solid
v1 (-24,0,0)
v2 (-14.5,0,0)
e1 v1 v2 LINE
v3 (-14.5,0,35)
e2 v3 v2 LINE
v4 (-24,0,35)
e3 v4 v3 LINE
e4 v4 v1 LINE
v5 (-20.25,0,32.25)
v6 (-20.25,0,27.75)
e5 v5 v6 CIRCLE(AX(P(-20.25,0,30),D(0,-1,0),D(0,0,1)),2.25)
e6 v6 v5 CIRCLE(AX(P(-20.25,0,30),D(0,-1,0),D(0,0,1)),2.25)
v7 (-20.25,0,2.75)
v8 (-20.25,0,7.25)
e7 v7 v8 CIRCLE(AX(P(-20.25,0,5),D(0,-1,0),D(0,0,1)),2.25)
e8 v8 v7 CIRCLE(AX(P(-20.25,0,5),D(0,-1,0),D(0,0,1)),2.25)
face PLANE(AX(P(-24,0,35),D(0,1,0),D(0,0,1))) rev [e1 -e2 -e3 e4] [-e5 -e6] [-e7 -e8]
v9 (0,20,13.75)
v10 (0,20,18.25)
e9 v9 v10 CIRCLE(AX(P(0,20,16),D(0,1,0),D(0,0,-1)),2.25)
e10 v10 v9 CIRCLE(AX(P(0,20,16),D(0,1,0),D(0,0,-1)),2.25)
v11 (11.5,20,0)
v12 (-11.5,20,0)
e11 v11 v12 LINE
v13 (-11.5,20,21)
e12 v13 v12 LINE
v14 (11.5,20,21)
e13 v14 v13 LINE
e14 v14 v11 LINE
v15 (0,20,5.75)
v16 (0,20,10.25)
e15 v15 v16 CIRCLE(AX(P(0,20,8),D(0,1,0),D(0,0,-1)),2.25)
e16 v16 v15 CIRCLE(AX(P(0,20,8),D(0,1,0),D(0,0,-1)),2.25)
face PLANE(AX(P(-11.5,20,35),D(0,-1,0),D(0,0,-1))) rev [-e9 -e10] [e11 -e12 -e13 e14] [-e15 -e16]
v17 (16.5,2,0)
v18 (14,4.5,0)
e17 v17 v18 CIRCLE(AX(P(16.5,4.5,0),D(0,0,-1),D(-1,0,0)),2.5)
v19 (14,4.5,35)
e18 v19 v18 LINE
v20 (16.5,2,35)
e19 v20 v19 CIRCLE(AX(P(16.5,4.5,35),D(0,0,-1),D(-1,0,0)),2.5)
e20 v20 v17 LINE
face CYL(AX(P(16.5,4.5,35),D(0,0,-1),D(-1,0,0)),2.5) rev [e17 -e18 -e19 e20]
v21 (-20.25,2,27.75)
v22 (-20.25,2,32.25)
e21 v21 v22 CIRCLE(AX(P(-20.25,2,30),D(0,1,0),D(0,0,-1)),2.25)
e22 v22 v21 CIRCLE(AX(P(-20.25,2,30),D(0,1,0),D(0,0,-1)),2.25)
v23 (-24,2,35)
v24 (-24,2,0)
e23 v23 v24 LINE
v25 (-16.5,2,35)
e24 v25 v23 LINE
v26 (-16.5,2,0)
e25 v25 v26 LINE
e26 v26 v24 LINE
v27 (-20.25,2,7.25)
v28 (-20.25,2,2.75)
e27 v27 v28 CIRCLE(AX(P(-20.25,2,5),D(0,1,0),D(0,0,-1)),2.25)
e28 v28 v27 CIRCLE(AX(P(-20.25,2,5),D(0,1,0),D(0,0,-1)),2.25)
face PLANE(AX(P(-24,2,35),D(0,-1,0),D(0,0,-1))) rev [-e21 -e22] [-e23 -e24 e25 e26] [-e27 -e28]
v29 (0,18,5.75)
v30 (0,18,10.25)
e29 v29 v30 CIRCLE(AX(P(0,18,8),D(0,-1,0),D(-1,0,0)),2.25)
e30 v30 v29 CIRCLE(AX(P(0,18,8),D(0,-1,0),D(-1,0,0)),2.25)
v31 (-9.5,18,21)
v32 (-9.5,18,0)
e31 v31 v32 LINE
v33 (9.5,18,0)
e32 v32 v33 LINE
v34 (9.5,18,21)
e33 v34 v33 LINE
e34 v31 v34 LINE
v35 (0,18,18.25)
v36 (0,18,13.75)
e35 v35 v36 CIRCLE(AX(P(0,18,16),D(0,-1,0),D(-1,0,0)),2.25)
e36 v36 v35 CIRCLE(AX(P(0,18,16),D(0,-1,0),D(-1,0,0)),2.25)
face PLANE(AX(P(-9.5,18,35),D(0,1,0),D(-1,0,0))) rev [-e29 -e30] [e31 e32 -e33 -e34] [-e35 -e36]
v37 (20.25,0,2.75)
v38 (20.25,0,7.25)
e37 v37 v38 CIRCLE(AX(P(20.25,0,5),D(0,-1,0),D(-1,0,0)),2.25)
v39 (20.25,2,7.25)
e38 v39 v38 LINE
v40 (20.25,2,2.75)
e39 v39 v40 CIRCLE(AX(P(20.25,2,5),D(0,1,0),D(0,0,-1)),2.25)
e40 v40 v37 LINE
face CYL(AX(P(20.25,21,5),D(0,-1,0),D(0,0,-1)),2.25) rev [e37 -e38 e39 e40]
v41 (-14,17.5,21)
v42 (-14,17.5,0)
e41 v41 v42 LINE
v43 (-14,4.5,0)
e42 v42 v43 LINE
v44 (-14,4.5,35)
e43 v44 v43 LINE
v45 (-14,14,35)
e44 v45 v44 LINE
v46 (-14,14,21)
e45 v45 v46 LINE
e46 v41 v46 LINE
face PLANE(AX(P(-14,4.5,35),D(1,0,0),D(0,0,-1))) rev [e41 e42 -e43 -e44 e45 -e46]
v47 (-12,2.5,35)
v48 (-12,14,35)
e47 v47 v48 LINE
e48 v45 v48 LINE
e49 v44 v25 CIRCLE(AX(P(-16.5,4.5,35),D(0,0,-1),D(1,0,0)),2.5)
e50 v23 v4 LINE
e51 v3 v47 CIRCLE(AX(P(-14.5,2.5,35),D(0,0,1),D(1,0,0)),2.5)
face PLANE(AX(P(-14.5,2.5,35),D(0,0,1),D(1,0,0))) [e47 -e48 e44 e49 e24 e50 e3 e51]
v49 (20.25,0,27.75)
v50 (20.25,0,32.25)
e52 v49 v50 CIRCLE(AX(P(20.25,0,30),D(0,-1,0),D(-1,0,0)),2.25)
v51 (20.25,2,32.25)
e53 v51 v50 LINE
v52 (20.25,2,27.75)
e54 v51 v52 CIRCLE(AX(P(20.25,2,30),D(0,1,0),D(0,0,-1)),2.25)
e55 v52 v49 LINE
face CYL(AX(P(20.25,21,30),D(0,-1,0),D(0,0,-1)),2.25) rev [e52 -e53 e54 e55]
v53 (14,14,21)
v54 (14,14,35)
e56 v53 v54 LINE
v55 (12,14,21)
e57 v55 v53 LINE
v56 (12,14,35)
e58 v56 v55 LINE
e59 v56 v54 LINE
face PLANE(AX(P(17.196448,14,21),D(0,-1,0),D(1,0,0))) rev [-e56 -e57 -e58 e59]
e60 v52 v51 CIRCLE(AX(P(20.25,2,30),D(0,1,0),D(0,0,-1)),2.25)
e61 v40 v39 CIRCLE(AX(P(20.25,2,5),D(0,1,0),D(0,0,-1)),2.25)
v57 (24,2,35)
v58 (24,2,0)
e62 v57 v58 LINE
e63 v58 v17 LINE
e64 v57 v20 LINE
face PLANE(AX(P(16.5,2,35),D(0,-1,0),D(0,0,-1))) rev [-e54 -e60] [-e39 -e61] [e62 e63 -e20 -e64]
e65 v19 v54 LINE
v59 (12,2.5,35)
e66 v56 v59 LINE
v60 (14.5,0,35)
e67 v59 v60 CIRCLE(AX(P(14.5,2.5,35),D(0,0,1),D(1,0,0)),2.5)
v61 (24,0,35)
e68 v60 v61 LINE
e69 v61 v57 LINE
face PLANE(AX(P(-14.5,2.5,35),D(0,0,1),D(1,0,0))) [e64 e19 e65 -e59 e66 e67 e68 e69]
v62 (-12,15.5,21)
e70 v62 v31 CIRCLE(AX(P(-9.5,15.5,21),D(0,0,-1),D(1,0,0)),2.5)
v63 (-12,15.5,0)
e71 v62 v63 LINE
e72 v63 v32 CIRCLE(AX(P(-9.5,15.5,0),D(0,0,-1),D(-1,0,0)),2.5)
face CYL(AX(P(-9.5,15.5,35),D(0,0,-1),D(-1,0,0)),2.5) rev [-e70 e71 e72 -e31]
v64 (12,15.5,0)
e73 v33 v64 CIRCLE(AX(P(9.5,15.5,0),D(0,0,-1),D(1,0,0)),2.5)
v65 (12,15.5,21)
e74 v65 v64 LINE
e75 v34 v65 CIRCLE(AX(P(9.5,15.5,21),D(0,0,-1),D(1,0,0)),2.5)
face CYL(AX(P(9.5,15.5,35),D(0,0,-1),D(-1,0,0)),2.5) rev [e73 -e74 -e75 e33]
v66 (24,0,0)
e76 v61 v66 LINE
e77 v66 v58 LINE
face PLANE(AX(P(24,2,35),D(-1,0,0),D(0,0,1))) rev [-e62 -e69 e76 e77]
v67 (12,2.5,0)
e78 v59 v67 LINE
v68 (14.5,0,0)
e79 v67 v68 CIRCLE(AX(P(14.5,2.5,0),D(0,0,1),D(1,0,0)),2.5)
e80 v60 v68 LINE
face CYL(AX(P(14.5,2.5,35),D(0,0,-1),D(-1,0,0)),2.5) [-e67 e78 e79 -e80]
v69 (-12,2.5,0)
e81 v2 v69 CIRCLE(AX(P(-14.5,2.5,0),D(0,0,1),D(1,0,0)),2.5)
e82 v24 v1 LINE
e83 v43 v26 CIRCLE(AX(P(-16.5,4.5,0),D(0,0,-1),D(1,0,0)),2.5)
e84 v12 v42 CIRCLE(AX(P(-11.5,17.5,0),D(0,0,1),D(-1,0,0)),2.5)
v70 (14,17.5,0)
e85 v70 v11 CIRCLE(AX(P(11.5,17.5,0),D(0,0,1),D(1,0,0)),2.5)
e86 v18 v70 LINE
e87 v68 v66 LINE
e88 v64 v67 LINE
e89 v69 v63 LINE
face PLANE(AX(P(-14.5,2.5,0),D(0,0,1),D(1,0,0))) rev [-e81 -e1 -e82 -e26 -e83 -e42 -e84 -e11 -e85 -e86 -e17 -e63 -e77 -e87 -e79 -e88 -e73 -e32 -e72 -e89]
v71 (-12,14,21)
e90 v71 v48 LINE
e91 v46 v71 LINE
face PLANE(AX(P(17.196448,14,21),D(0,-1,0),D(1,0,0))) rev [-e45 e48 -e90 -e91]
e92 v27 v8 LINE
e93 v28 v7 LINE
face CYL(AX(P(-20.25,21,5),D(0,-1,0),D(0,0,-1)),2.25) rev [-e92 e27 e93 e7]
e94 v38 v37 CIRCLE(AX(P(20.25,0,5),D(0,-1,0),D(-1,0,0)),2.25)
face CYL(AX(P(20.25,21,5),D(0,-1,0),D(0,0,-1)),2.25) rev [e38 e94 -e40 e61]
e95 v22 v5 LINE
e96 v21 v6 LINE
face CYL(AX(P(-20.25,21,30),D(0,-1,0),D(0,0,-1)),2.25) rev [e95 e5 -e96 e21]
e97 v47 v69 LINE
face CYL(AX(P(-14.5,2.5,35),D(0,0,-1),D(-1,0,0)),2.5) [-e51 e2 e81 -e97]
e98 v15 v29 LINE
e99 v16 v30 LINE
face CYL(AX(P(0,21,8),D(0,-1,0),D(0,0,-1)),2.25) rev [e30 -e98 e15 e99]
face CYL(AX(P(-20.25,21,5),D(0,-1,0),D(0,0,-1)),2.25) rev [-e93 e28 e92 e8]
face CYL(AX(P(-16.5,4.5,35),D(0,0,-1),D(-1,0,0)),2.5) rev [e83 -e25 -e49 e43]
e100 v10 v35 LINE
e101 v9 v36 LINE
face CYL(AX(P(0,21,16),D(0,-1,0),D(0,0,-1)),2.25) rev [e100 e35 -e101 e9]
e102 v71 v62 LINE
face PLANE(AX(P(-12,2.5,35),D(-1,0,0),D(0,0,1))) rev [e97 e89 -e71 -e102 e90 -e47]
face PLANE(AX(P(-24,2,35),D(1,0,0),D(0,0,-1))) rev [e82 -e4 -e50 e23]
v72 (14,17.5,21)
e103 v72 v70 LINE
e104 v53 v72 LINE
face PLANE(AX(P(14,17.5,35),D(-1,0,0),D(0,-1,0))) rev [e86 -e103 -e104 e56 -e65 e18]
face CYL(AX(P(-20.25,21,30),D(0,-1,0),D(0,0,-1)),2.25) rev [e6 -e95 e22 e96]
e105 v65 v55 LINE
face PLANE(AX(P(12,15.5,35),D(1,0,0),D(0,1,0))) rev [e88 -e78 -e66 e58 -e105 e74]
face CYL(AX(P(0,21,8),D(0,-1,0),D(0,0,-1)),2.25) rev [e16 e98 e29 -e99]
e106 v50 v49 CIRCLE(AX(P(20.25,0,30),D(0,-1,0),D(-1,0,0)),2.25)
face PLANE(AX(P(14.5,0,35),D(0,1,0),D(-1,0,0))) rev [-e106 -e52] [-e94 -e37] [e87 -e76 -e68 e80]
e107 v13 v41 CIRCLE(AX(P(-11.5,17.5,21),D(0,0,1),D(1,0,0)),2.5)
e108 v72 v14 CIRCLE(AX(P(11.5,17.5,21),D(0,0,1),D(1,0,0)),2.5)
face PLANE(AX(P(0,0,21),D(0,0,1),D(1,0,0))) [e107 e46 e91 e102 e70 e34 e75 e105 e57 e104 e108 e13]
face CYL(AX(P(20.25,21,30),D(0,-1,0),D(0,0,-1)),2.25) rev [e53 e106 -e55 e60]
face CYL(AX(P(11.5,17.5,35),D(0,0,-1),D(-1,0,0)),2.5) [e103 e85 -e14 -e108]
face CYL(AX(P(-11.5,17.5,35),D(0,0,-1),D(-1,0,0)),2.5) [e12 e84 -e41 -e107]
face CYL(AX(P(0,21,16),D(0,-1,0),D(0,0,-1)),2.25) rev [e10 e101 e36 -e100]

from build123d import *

# Parameters (mm, degrees)
BOSS_EXTRUDE1_DEPTH = 35
SKETCH2_W           = 34.392896322
SKETCH2_H           = 15.037586703
CUT_EXTRUDE1_DEPTH  = 14
SKETCH3_R           = 2.25
CUT_EXTRUDE2_DEPTH  = 19


with BuildPart() as part:
    # Sketch1 → Boss-Extrude1 (new body)
    with BuildSketch(Plane.XY):
        with BuildLine():
            Line((-24, 0), (-14.5, 0))
            ThreePointArc((-14.5, 0), (-12.732233047, 0.732233047), (-12, 2.5))
            Line((-12, 2.5), (-12, 15.5))
            ThreePointArc((-12, 15.5), (-11.267766953, 17.267766953), (-9.5, 18))
            Line((-9.5, 18), (9.5, 18))
            ThreePointArc((9.5, 18), (11.267766953, 17.267766953), (12, 15.5))
            Line((12, 15.5), (12, 2.5))
            ThreePointArc((12, 2.5), (12.732233047, 0.732233047), (14.5, 0))
            Line((14.5, 0), (24, 0))
            Line((24, 0), (24, 2))
            Line((24, 2), (16.5, 2))
            ThreePointArc((16.5, 2), (14.732233047, 2.732233047), (14, 4.5))
            Line((14, 4.5), (14, 17.5))
            ThreePointArc((14, 17.5), (13.267766953, 19.267766953), (11.5, 20))
            Line((11.5, 20), (-11.5, 20))
            ThreePointArc((-11.5, 20), (-13.267766953, 19.267766953), (-14, 17.5))
            Line((-14, 17.5), (-14, 4.5))
            ThreePointArc((-14, 4.5), (-14.732233047, 2.732233047), (-16.5, 2))
            Line((-16.5, 2), (-24, 2))
            Line((-24, 2), (-24, 0))
        make_face()
    extrude(amount=BOSS_EXTRUDE1_DEPTH)

    # Sketch2 → Cut-Extrude1 (cut)
    with BuildSketch(Plane.XY.offset(35)):
        with Locations((0, 21.518793352)):
            Rectangle(SKETCH2_W, SKETCH2_H)
    extrude(amount=-CUT_EXTRUDE1_DEPTH, mode=Mode.SUBTRACT)

    # Sketch3 → Cut-Extrude2 (cut, symmetric)
    with BuildSketch(Plane(origin=(0, 2, 0), x_dir=(1, 0, 0), z_dir=(0, 1, 0))):
        with Locations(Location((-20.25, -5, 0), (0, 0, 90))):
            Circle(SKETCH3_R)
        with Locations(Location((-20.25, -30, 0), (0, 0, 90))):
            Circle(SKETCH3_R)
        with Locations(Location((20.25, -30, 0), (0, 0, 90))):
            Circle(SKETCH3_R)
        with Locations(Location((20.25, -5, 0), (0, 0, 90))):
            Circle(SKETCH3_R)
        with Locations(Location((0, -8, 0), (0, 0, 90))):
            Circle(SKETCH3_R)
        with Locations(Location((0, -16, 0), (0, 0, 90))):
            Circle(SKETCH3_R)
    extrude(amount=CUT_EXTRUDE2_DEPTH, both=True, mode=Mode.SUBTRACT)


solid = part.part
